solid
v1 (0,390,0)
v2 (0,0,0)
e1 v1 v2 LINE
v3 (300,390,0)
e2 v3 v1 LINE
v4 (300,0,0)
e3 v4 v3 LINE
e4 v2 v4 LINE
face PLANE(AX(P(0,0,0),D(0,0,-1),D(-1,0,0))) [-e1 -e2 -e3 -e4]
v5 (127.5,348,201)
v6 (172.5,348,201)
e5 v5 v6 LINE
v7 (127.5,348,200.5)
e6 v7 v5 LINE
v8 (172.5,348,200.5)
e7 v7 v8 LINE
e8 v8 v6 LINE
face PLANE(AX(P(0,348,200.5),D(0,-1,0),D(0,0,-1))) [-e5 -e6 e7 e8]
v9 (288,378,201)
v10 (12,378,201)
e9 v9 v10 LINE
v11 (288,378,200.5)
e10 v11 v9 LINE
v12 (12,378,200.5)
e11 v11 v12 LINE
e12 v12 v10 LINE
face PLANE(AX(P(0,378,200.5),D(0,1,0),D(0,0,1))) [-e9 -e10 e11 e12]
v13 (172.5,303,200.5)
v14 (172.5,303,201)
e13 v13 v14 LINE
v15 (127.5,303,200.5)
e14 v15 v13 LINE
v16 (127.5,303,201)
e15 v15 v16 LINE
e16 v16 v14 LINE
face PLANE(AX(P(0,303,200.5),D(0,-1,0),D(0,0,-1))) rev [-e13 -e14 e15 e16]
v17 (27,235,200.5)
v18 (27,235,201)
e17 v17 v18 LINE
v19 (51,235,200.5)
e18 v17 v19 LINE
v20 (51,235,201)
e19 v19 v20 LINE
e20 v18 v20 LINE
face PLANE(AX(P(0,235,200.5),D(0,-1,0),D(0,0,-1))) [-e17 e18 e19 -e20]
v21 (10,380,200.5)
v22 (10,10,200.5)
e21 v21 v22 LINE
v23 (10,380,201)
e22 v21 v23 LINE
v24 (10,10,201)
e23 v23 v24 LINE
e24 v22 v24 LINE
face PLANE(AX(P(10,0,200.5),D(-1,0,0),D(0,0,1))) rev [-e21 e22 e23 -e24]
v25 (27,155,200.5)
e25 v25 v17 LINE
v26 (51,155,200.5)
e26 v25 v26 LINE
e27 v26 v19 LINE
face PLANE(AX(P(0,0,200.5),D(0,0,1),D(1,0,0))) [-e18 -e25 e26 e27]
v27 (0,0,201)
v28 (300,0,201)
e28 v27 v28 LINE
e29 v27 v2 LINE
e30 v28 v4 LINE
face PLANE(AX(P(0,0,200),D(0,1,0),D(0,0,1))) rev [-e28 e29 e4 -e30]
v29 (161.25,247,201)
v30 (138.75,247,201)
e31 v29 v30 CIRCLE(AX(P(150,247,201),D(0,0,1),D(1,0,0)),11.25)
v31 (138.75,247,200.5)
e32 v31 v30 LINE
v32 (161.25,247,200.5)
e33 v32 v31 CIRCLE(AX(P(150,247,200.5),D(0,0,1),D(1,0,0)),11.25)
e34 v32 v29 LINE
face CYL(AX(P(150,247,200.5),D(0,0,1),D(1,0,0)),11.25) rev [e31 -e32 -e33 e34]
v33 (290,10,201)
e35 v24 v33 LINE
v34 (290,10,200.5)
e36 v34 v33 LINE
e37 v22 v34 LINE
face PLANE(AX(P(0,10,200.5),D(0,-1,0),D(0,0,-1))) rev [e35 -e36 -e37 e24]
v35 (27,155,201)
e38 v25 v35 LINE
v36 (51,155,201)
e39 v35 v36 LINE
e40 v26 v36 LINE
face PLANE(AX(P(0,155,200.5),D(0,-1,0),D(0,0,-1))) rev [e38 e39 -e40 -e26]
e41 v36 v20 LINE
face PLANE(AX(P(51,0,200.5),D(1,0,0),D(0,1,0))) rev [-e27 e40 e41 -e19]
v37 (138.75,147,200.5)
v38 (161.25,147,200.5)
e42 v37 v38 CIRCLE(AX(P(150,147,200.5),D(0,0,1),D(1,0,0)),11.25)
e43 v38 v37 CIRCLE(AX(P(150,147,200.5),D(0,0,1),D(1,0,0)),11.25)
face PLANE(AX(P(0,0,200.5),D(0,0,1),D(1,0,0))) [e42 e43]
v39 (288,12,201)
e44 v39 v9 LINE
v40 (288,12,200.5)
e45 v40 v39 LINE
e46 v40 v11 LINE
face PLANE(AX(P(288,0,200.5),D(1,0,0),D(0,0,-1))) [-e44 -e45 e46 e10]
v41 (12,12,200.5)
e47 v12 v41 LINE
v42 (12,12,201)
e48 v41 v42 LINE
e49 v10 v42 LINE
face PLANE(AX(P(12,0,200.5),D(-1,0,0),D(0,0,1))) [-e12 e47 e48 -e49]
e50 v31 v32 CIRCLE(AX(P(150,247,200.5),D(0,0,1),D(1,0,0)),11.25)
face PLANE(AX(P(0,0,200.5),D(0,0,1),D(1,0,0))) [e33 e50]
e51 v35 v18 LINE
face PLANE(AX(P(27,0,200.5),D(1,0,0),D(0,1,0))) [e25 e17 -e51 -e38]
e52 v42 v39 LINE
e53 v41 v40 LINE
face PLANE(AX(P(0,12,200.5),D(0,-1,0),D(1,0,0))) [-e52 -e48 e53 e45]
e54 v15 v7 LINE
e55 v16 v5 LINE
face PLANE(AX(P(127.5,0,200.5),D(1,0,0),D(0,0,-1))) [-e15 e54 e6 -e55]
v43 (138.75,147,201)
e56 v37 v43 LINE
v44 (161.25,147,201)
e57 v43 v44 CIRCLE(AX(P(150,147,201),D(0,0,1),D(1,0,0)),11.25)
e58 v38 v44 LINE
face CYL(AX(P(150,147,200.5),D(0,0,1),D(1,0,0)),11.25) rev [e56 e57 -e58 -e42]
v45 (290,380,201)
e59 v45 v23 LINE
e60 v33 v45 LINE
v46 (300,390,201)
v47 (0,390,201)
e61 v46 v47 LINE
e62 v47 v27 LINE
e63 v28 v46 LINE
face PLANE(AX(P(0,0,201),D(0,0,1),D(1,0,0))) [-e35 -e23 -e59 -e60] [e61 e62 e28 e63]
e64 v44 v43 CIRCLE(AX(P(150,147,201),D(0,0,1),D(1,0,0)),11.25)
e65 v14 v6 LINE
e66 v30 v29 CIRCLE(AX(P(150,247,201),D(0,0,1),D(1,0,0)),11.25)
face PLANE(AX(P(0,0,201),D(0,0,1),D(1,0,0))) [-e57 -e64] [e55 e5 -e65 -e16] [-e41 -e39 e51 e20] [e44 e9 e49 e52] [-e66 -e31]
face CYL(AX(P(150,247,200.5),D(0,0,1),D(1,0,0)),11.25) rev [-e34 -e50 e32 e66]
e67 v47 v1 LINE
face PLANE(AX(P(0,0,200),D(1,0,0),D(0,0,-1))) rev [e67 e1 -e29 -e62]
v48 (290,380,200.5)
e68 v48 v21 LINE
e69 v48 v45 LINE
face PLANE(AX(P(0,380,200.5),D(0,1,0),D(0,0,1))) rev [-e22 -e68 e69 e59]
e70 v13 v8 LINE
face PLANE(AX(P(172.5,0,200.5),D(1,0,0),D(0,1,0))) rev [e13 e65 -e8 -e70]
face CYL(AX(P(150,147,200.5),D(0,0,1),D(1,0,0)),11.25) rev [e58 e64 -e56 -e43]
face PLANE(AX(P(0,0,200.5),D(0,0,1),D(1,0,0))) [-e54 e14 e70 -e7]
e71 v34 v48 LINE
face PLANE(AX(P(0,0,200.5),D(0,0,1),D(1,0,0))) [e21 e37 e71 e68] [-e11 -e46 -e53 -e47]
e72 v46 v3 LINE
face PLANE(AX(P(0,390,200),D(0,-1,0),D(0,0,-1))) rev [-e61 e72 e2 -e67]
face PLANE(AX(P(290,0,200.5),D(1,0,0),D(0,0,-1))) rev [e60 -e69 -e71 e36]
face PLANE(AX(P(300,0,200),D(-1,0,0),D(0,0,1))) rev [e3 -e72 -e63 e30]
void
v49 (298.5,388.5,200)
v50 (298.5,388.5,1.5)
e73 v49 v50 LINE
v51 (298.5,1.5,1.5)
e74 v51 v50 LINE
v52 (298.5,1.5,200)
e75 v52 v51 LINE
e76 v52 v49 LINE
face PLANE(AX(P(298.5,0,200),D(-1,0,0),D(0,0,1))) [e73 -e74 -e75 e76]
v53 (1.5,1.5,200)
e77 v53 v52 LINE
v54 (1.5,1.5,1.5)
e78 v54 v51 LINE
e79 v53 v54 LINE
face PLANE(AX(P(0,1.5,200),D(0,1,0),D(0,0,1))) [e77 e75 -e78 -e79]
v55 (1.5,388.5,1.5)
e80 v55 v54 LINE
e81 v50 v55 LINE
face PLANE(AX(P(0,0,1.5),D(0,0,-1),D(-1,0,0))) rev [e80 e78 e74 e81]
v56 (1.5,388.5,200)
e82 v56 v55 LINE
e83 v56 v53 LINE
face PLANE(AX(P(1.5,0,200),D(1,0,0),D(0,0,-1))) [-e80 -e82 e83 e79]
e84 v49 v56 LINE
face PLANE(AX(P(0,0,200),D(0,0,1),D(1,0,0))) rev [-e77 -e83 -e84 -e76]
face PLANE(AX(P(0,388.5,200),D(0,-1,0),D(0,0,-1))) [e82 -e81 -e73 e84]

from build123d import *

# Parameters (mm, degrees)
SKETCH1_W           = 300
SKETCH1_H           = 390
BOSS_EXTRUDE1_DEPTH = 200
SHELL1_T            = -1.5
SKETCH2_W           = 300
SKETCH2_H           = 390
BOSS_EXTRUDE2_DEPTH = 1
SKETCH3_W           = 280
SKETCH3_H           = 370
SKETCH3_W_2         = 276
SKETCH3_H_2         = 366
SKETCH3_R           = 11.25
SKETCH3_W_3         = 24
SKETCH3_H_3         = 80
SKETCH3_W_4         = 45
SKETCH3_H_4         = 45
CUT_EXTRUDE1_DEPTH  = 0.5


with BuildPart() as part:
    # Sketch1 → Boss-Extrude1 (new body)
    with BuildSketch(Plane.XY):
        with Locations((150, 195)):
            Rectangle(SKETCH1_W, SKETCH1_H)
    extrude(amount=BOSS_EXTRUDE1_DEPTH)

    # Shell1
    shell1_openings = [part.faces().sort_by_distance(p)[0] for p in [
        (150, 195, 200),
    ]]
    offset(amount=SHELL1_T, openings=shell1_openings, kind=Kind.INTERSECTION)

    # Sketch2 → Boss-Extrude2 (add)
    with BuildSketch(Plane.XY.offset(200)):
        with Locations((150, 195)):
            Rectangle(SKETCH2_W, SKETCH2_H)
    extrude(amount=BOSS_EXTRUDE2_DEPTH)

    # Sketch3 → Cut-Extrude1 (cut)
    # profile 1 of 5: a face of its own
    with BuildSketch(Plane.XY.offset(201)):
        with Locations((150, 195)):
            Rectangle(SKETCH3_W, SKETCH3_H)
        with Locations((150, 195)):
            Rectangle(SKETCH3_W_2, SKETCH3_H_2, mode=Mode.SUBTRACT)
    # profile 2 of 5: a face of its own
    with BuildSketch(Plane.XY.offset(201)):
        with Locations((150, 247)):
            Circle(SKETCH3_R)
    # profile 3 of 5: a face of its own
    with BuildSketch(Plane.XY.offset(201)):
        with Locations((150, 147)):
            Circle(SKETCH3_R)
    # profile 4 of 5: a face of its own
    with BuildSketch(Plane.XY.offset(201)):
        with Locations((39, 195)):
            Rectangle(SKETCH3_W_3, SKETCH3_H_3)
    # profile 5 of 5: a face of its own
    with BuildSketch(Plane.XY.offset(201)):
        with Locations((150, 325.5)):
            Rectangle(SKETCH3_W_4, SKETCH3_H_4)
    extrude(amount=-CUT_EXTRUDE1_DEPTH, mode=Mode.SUBTRACT)


solid = part.part
